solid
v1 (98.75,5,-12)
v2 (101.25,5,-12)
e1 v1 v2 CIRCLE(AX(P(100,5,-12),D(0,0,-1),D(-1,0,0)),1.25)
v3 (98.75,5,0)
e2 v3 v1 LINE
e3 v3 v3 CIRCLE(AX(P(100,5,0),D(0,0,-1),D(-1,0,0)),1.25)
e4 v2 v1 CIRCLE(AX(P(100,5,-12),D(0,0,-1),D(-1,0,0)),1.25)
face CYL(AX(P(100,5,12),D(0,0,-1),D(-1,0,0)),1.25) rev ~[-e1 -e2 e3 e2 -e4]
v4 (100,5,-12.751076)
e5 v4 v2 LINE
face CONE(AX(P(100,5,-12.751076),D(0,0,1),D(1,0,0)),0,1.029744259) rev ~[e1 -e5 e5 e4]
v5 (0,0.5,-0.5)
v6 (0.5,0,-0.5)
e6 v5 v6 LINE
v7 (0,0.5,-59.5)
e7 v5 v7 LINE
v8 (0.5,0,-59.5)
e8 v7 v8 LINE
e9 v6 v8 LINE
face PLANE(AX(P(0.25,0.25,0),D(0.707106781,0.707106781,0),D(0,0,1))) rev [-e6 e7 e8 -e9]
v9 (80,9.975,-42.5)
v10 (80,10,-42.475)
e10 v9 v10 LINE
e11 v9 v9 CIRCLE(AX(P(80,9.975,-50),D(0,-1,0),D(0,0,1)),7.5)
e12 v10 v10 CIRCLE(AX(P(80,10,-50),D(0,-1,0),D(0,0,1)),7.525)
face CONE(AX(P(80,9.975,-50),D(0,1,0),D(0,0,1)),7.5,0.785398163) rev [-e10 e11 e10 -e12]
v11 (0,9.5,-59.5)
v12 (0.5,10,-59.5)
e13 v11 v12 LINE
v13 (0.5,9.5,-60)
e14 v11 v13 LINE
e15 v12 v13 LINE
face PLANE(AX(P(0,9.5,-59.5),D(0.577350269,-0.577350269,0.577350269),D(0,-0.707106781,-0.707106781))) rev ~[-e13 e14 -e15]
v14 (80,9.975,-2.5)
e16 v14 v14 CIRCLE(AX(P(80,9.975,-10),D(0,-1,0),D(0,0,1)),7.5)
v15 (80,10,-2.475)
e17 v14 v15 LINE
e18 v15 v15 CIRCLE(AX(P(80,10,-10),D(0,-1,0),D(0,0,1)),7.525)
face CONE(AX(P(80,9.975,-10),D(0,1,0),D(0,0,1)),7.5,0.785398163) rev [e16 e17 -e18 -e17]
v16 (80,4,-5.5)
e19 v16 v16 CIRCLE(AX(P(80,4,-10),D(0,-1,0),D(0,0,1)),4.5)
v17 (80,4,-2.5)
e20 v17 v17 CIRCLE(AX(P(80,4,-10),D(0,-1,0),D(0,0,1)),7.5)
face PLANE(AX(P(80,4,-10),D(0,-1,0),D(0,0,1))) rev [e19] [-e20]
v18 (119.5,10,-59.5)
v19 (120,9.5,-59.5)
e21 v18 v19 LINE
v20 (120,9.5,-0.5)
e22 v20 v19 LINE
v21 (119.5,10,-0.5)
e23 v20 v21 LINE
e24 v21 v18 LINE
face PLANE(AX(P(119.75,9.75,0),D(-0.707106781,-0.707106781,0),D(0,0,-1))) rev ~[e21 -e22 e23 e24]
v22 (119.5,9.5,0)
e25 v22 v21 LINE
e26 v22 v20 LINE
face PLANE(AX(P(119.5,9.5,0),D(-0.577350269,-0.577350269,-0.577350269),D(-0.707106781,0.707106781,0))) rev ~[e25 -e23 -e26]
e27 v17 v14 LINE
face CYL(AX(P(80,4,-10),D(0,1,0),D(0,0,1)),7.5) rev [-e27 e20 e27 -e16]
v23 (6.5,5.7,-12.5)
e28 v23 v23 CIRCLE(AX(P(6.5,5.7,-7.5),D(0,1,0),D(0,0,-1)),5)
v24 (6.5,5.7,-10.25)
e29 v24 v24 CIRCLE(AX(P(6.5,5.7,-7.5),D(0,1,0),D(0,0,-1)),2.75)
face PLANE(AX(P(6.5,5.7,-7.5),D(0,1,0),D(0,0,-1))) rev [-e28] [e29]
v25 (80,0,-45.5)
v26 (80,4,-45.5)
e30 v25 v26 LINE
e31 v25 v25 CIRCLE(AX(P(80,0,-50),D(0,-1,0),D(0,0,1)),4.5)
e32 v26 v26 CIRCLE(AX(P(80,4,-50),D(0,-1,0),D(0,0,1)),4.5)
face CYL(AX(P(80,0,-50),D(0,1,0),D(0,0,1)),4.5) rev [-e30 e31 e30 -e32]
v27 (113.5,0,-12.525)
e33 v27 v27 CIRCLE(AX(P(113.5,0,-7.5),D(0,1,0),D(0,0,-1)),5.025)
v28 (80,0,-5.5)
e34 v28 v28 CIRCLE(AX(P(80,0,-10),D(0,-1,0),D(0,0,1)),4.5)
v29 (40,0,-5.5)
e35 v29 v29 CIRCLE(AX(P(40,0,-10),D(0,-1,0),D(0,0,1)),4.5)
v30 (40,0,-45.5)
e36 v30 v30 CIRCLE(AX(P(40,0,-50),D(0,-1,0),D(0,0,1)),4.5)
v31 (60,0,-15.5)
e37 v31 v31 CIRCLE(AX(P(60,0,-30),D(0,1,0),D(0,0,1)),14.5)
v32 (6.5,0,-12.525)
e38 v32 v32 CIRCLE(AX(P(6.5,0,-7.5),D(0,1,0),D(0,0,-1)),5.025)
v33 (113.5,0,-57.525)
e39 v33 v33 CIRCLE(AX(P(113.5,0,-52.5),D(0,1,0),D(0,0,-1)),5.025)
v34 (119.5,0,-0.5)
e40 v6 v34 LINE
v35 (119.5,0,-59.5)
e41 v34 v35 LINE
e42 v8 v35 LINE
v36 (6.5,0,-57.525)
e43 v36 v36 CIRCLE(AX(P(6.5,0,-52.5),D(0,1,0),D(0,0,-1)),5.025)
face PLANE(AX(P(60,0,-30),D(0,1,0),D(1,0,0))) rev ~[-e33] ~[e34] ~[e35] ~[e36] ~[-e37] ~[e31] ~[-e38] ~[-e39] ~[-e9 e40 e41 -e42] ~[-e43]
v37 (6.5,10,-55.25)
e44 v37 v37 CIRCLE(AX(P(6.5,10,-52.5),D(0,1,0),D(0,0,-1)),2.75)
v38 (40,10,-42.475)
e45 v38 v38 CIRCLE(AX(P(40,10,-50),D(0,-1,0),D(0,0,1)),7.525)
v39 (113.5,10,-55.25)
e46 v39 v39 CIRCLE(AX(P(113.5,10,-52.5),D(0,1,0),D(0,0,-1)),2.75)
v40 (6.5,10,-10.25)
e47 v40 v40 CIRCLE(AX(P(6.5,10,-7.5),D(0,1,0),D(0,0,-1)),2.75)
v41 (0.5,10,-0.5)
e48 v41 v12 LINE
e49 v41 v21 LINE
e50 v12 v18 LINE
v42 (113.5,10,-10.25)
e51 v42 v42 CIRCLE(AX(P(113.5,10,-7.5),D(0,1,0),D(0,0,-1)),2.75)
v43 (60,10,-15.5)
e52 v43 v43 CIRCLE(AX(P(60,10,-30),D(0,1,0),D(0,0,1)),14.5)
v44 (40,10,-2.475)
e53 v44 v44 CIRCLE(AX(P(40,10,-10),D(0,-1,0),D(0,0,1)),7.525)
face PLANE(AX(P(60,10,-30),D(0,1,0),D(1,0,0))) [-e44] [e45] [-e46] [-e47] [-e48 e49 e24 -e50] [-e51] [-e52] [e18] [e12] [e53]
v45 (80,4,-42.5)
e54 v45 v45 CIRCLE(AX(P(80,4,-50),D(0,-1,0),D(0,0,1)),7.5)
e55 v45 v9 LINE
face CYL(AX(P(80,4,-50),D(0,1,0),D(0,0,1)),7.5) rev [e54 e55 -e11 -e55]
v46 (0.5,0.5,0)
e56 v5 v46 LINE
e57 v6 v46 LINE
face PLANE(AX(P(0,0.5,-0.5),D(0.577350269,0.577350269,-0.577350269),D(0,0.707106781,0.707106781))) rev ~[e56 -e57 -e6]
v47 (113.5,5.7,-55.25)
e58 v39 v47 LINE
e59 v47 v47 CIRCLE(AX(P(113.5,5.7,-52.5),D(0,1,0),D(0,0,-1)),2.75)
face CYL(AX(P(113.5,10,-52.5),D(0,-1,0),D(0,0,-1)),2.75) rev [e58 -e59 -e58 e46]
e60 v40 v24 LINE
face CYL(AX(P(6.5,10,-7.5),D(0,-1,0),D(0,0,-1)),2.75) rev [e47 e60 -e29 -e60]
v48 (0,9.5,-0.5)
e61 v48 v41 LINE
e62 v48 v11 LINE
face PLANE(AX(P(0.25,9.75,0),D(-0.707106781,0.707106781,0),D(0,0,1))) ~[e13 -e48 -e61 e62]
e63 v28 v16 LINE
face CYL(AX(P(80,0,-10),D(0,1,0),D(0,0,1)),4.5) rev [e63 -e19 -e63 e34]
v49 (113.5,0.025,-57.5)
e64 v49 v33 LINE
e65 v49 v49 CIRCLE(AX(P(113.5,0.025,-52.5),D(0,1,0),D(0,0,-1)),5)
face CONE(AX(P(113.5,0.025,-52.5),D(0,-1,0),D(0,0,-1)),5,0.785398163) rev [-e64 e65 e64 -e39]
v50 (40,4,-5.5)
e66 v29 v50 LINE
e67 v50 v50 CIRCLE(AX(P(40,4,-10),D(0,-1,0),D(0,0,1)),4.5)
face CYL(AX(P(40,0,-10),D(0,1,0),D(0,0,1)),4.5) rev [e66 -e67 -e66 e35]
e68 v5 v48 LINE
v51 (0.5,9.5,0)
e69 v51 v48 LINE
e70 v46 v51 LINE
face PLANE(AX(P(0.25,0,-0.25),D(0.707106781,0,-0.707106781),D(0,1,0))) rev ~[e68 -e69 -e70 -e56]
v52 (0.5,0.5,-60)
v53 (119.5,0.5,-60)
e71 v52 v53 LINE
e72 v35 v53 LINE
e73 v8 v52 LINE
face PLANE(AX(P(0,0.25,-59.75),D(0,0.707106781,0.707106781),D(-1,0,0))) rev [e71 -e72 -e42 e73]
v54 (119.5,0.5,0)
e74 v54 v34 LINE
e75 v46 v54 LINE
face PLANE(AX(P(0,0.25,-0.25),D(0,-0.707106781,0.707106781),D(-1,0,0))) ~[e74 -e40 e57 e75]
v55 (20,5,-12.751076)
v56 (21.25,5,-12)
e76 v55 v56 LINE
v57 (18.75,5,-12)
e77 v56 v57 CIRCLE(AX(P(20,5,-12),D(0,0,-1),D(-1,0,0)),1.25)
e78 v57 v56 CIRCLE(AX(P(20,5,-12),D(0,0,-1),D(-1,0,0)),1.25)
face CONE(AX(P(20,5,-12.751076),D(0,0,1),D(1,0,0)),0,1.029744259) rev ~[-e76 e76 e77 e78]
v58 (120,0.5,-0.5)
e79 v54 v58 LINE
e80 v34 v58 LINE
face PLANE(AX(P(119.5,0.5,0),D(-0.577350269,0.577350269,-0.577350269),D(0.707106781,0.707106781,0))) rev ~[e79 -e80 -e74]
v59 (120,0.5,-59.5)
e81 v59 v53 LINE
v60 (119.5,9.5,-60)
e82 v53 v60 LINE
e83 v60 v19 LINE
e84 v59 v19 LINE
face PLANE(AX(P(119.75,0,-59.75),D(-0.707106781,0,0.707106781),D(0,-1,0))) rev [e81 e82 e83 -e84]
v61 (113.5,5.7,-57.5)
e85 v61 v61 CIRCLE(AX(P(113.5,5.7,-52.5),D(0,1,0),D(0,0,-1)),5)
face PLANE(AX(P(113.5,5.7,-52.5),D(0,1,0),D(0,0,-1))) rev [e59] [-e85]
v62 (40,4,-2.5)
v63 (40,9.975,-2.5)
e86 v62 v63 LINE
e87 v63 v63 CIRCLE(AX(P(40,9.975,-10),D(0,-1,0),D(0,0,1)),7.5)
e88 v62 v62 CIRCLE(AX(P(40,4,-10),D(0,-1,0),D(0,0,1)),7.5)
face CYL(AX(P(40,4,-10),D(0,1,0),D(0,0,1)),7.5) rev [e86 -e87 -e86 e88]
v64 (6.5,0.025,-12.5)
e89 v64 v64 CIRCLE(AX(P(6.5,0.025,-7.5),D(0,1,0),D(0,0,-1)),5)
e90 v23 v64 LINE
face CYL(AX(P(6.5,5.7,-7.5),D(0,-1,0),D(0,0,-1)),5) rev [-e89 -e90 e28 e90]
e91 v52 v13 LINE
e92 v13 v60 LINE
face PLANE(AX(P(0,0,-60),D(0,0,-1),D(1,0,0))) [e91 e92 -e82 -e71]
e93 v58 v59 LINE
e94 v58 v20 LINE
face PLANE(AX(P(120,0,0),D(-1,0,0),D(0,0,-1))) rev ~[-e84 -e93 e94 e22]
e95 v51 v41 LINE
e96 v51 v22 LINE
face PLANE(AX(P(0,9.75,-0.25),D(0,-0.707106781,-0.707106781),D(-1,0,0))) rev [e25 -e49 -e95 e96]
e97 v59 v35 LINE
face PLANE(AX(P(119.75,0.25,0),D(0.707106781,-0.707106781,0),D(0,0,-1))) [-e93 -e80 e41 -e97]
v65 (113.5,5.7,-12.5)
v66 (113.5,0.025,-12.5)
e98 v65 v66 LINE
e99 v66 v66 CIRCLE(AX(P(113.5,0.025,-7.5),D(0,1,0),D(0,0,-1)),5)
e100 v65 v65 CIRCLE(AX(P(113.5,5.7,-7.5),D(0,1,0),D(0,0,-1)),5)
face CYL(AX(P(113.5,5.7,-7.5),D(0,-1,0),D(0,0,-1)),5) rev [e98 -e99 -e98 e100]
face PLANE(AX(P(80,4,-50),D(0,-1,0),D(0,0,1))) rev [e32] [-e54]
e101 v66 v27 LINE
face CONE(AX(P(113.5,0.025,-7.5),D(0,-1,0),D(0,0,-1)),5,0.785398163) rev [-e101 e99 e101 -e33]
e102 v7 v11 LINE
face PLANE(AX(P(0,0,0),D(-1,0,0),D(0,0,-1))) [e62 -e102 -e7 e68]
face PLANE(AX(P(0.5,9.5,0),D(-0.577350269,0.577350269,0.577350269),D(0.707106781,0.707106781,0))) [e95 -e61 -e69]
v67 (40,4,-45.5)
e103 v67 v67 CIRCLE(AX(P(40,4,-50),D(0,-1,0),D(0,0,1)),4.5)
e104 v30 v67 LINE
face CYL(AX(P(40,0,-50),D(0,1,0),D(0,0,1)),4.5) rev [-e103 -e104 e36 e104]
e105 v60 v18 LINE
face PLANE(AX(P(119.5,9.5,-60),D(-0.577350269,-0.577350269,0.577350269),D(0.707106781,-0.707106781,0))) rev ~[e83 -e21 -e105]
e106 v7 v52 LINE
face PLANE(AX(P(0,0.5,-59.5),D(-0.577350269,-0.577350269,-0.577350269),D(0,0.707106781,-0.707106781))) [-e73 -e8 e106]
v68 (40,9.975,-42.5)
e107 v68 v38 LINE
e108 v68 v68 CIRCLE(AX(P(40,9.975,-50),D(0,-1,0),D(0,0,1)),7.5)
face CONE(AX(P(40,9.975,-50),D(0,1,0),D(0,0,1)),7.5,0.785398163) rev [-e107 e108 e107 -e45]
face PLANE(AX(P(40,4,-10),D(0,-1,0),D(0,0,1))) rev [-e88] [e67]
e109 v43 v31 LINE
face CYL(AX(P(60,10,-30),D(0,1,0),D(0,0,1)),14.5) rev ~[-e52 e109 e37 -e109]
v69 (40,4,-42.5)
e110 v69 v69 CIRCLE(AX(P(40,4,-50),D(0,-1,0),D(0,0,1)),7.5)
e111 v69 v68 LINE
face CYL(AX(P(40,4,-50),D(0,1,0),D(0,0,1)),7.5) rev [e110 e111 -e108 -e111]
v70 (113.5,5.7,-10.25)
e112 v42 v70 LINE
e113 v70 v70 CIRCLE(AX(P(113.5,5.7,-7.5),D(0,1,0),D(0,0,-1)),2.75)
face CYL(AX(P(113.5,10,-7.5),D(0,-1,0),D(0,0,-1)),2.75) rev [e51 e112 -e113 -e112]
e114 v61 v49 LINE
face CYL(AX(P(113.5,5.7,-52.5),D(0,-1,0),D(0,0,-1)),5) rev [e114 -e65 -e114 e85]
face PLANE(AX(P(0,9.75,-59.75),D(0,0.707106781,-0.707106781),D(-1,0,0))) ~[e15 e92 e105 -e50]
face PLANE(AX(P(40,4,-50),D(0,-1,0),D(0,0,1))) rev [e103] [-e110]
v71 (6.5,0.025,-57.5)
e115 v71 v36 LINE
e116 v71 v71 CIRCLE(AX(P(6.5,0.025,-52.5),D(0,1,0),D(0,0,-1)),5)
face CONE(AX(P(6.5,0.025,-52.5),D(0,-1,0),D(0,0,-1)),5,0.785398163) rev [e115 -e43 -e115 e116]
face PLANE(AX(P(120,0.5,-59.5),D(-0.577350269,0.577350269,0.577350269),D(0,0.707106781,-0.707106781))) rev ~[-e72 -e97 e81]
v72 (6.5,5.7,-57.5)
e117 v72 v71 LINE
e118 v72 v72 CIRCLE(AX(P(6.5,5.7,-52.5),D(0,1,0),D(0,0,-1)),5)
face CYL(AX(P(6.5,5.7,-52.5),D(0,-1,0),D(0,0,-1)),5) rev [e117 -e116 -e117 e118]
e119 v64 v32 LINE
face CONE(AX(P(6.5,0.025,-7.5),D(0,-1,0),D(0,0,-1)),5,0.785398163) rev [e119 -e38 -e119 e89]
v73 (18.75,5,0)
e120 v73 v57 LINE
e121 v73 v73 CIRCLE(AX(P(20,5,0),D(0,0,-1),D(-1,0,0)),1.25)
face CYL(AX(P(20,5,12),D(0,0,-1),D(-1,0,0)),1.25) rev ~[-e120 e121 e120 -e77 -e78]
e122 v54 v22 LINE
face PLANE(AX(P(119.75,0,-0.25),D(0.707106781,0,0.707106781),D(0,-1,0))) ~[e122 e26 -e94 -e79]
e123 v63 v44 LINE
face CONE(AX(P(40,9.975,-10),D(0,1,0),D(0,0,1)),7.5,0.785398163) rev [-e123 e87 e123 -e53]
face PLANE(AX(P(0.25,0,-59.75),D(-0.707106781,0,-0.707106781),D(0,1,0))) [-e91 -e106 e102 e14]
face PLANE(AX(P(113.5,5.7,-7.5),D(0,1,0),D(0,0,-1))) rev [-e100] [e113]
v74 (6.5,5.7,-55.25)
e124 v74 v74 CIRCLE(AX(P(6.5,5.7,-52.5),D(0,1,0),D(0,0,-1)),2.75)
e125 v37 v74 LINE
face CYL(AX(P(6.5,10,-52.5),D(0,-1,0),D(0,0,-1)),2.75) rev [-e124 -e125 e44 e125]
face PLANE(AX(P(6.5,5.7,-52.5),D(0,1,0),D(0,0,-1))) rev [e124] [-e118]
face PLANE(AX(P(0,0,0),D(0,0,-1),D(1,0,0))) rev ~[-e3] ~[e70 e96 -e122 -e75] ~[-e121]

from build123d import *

# Parameters (mm, degrees)
SKETCH1_W                                    = 120
SKETCH1_H                                    = 60
BOSS_EXTRUDE1_DEPTH                          = 10
SKETCH2_R                                    = 14.5
CUT_EXTRUDE1_DEPTH                           = 10
CBORE_FOR_M8_SLOTTED_CHEESE_HEAD_SCR_2_COUNT = 2
CBORE_FOR_M8_SLOTTED_CHEESE_HEAD_SCR_2_PITCH = 56.568542495
CBORE_FOR_M8_SLOTTED_CHEESE_HEAD_SCR_3_COUNT = 2
CBORE_FOR_M8_SLOTTED_CHEESE_HEAD_SCR_3_PITCH = 40
CBORE_FOR_M8_SLOTTED_CHEESE_HEAD_SCR_4_COUNT = 2
CBORE_FOR_M8_SLOTTED_CHEESE_HEAD_SCR_4_PITCH = 40
CBORE_FOR_M5_SLOTTED_CHEESE_HEAD_SCR_2_COUNT = 2
CBORE_FOR_M5_SLOTTED_CHEESE_HEAD_SCR_2_PITCH = 45
CBORE_FOR_M5_SLOTTED_CHEESE_HEAD_SCR_3_COUNT = 2
CBORE_FOR_M5_SLOTTED_CHEESE_HEAD_SCR_3_PITCH = 107
CBORE_FOR_M5_SLOTTED_CHEESE_HEAD_SCR_4_COUNT = 2
CBORE_FOR_M5_SLOTTED_CHEESE_HEAD_SCR_4_PITCH = 116.077560278
M3_TAPPED_HOLE1_D                            = 2.5
M3_TAPPED_HOLE1_DEPTH                        = 12
M3_TAPPED_HOLE1_TIP                          = 0.751075774
CHAMFER1_SIZE                                = 0.5


with BuildPart() as part:
    # Sketch1 → Boss-Extrude1 (new body)
    with BuildSketch(Plane(origin=(0, 0, 0), x_dir=(1, 0, 0), z_dir=(0, 1, 0))):
        with Locations((60, 30)):
            Rectangle(SKETCH1_W, SKETCH1_H)
    extrude(amount=BOSS_EXTRUDE1_DEPTH)

    # Sketch2 → Cut-Extrude1 (cut)
    with BuildSketch(Plane(origin=(0, 10, 0), x_dir=(1, 0, 0), z_dir=(0, 1, 0))):
        with Locations(Location((60, 30, 0), (0, 0, 270))):
            Circle(SKETCH2_R)
    extrude(amount=-CUT_EXTRUDE1_DEPTH, mode=Mode.SUBTRACT)

    # Sketch5 → CBORE for M8 Slotted cheese head screws1 (revolve, cut)
    with BuildSketch(Plane(origin=(80, 10, -10), x_dir=(0, 0, 1), z_dir=(1, 0, 0))):
        Polygon((0, 0), (0, 10), (4.5, 10), (4.5, 6), (7.5, 6), (7.5, 0.025), (7.525, 0), align=None)
    cbore_for_m8_slotted_cheese_head_screws1 = revolve(axis=Axis((80, 16.35, -10), (0, -1, 0)), mode=Mode.SUBTRACT)

    # CBORE for M8 Slotted cheese head scr 2: CBORE for M8 Slotted cheese head screws1 ×2
    with Locations(*[Vector(-0.7071067811865476, 0, -0.7071067811865476) * (i * CBORE_FOR_M8_SLOTTED_CHEESE_HEAD_SCR_2_PITCH) for i in range(1, CBORE_FOR_M8_SLOTTED_CHEESE_HEAD_SCR_2_COUNT)]):
        add(cbore_for_m8_slotted_cheese_head_screws1, mode=Mode.SUBTRACT)

    # CBORE for M8 Slotted cheese head scr 3: CBORE for M8 Slotted cheese head screws1 ×2
    with Locations(*[(0, 0, -i * CBORE_FOR_M8_SLOTTED_CHEESE_HEAD_SCR_3_PITCH) for i in range(1, CBORE_FOR_M8_SLOTTED_CHEESE_HEAD_SCR_3_COUNT)]):
        add(cbore_for_m8_slotted_cheese_head_screws1, mode=Mode.SUBTRACT)

    # CBORE for M8 Slotted cheese head scr 4: CBORE for M8 Slotted cheese head screws1 ×2
    with Locations(*[(-i * CBORE_FOR_M8_SLOTTED_CHEESE_HEAD_SCR_4_PITCH, 0, 0) for i in range(1, CBORE_FOR_M8_SLOTTED_CHEESE_HEAD_SCR_4_COUNT)]):
        add(cbore_for_m8_slotted_cheese_head_screws1, mode=Mode.SUBTRACT)

    # Sketch7 → CBORE for M5 Slotted cheese head screws1 (revolve, cut)
    with BuildSketch(Plane(origin=(6.5, 0, -7.5), x_dir=(0, 0, -1), z_dir=(1, 0, 0))):
        Polygon((0, 0), (0, 10), (2.75, 10), (2.75, 5.7), (5, 5.7), (5, 0.025), (5.025, 0), align=None)
    cbore_for_m5_slotted_cheese_head_screws1 = revolve(axis=Axis((6.5, -6.35, -7.5), (0, 1, 0)), mode=Mode.SUBTRACT)

    # CBORE for M5 Slotted cheese head scr 2: CBORE for M5 Slotted cheese head screws1 ×2
    with Locations(*[(0, 0, -i * CBORE_FOR_M5_SLOTTED_CHEESE_HEAD_SCR_2_PITCH) for i in range(1, CBORE_FOR_M5_SLOTTED_CHEESE_HEAD_SCR_2_COUNT)]):
        add(cbore_for_m5_slotted_cheese_head_screws1, mode=Mode.SUBTRACT)

    # CBORE for M5 Slotted cheese head scr 3: CBORE for M5 Slotted cheese head screws1 ×2
    with Locations(*[(i * CBORE_FOR_M5_SLOTTED_CHEESE_HEAD_SCR_3_PITCH, 0, 0) for i in range(1, CBORE_FOR_M5_SLOTTED_CHEESE_HEAD_SCR_3_COUNT)]):
        add(cbore_for_m5_slotted_cheese_head_screws1, mode=Mode.SUBTRACT)

    # CBORE for M5 Slotted cheese head scr 4: CBORE for M5 Slotted cheese head screws1 ×2
    with Locations(*[Vector(0.9217974580453662, 0, -0.3876718281499204) * (i * CBORE_FOR_M5_SLOTTED_CHEESE_HEAD_SCR_4_PITCH) for i in range(1, CBORE_FOR_M5_SLOTTED_CHEESE_HEAD_SCR_4_COUNT)]):
        add(cbore_for_m5_slotted_cheese_head_screws1, mode=Mode.SUBTRACT)

    # M3 Tapped Hole1
    with Locations(Plane.XY):
        with Locations((20, 5), (100, 5)):
            Hole(M3_TAPPED_HOLE1_D / 2, depth=M3_TAPPED_HOLE1_DEPTH)
            with Locations((0, 0, -(M3_TAPPED_HOLE1_DEPTH + M3_TAPPED_HOLE1_TIP / 2))):  # 118° drill point
                Cone(0, M3_TAPPED_HOLE1_D / 2, M3_TAPPED_HOLE1_TIP, mode=Mode.SUBTRACT)

    # Chamfer1
    chamfer1_edges = [part.edges().sort_by_distance(p)[0] for p in [
        (120, 10, -30),
        (60, 10, -60),
        (0, 10, -30),
        (60, 0, -60),
        (120, 0, -30),
        (60, 0, 0),
        (0, 0, -30),
        (0, 5, -60),
        (120, 5, -60),
        (120, 5, 0),
        (0, 5, 0),
        (60, 10, 0),
    ]]
    chamfer(chamfer1_edges, length=CHAMFER1_SIZE)


solid = part.part
